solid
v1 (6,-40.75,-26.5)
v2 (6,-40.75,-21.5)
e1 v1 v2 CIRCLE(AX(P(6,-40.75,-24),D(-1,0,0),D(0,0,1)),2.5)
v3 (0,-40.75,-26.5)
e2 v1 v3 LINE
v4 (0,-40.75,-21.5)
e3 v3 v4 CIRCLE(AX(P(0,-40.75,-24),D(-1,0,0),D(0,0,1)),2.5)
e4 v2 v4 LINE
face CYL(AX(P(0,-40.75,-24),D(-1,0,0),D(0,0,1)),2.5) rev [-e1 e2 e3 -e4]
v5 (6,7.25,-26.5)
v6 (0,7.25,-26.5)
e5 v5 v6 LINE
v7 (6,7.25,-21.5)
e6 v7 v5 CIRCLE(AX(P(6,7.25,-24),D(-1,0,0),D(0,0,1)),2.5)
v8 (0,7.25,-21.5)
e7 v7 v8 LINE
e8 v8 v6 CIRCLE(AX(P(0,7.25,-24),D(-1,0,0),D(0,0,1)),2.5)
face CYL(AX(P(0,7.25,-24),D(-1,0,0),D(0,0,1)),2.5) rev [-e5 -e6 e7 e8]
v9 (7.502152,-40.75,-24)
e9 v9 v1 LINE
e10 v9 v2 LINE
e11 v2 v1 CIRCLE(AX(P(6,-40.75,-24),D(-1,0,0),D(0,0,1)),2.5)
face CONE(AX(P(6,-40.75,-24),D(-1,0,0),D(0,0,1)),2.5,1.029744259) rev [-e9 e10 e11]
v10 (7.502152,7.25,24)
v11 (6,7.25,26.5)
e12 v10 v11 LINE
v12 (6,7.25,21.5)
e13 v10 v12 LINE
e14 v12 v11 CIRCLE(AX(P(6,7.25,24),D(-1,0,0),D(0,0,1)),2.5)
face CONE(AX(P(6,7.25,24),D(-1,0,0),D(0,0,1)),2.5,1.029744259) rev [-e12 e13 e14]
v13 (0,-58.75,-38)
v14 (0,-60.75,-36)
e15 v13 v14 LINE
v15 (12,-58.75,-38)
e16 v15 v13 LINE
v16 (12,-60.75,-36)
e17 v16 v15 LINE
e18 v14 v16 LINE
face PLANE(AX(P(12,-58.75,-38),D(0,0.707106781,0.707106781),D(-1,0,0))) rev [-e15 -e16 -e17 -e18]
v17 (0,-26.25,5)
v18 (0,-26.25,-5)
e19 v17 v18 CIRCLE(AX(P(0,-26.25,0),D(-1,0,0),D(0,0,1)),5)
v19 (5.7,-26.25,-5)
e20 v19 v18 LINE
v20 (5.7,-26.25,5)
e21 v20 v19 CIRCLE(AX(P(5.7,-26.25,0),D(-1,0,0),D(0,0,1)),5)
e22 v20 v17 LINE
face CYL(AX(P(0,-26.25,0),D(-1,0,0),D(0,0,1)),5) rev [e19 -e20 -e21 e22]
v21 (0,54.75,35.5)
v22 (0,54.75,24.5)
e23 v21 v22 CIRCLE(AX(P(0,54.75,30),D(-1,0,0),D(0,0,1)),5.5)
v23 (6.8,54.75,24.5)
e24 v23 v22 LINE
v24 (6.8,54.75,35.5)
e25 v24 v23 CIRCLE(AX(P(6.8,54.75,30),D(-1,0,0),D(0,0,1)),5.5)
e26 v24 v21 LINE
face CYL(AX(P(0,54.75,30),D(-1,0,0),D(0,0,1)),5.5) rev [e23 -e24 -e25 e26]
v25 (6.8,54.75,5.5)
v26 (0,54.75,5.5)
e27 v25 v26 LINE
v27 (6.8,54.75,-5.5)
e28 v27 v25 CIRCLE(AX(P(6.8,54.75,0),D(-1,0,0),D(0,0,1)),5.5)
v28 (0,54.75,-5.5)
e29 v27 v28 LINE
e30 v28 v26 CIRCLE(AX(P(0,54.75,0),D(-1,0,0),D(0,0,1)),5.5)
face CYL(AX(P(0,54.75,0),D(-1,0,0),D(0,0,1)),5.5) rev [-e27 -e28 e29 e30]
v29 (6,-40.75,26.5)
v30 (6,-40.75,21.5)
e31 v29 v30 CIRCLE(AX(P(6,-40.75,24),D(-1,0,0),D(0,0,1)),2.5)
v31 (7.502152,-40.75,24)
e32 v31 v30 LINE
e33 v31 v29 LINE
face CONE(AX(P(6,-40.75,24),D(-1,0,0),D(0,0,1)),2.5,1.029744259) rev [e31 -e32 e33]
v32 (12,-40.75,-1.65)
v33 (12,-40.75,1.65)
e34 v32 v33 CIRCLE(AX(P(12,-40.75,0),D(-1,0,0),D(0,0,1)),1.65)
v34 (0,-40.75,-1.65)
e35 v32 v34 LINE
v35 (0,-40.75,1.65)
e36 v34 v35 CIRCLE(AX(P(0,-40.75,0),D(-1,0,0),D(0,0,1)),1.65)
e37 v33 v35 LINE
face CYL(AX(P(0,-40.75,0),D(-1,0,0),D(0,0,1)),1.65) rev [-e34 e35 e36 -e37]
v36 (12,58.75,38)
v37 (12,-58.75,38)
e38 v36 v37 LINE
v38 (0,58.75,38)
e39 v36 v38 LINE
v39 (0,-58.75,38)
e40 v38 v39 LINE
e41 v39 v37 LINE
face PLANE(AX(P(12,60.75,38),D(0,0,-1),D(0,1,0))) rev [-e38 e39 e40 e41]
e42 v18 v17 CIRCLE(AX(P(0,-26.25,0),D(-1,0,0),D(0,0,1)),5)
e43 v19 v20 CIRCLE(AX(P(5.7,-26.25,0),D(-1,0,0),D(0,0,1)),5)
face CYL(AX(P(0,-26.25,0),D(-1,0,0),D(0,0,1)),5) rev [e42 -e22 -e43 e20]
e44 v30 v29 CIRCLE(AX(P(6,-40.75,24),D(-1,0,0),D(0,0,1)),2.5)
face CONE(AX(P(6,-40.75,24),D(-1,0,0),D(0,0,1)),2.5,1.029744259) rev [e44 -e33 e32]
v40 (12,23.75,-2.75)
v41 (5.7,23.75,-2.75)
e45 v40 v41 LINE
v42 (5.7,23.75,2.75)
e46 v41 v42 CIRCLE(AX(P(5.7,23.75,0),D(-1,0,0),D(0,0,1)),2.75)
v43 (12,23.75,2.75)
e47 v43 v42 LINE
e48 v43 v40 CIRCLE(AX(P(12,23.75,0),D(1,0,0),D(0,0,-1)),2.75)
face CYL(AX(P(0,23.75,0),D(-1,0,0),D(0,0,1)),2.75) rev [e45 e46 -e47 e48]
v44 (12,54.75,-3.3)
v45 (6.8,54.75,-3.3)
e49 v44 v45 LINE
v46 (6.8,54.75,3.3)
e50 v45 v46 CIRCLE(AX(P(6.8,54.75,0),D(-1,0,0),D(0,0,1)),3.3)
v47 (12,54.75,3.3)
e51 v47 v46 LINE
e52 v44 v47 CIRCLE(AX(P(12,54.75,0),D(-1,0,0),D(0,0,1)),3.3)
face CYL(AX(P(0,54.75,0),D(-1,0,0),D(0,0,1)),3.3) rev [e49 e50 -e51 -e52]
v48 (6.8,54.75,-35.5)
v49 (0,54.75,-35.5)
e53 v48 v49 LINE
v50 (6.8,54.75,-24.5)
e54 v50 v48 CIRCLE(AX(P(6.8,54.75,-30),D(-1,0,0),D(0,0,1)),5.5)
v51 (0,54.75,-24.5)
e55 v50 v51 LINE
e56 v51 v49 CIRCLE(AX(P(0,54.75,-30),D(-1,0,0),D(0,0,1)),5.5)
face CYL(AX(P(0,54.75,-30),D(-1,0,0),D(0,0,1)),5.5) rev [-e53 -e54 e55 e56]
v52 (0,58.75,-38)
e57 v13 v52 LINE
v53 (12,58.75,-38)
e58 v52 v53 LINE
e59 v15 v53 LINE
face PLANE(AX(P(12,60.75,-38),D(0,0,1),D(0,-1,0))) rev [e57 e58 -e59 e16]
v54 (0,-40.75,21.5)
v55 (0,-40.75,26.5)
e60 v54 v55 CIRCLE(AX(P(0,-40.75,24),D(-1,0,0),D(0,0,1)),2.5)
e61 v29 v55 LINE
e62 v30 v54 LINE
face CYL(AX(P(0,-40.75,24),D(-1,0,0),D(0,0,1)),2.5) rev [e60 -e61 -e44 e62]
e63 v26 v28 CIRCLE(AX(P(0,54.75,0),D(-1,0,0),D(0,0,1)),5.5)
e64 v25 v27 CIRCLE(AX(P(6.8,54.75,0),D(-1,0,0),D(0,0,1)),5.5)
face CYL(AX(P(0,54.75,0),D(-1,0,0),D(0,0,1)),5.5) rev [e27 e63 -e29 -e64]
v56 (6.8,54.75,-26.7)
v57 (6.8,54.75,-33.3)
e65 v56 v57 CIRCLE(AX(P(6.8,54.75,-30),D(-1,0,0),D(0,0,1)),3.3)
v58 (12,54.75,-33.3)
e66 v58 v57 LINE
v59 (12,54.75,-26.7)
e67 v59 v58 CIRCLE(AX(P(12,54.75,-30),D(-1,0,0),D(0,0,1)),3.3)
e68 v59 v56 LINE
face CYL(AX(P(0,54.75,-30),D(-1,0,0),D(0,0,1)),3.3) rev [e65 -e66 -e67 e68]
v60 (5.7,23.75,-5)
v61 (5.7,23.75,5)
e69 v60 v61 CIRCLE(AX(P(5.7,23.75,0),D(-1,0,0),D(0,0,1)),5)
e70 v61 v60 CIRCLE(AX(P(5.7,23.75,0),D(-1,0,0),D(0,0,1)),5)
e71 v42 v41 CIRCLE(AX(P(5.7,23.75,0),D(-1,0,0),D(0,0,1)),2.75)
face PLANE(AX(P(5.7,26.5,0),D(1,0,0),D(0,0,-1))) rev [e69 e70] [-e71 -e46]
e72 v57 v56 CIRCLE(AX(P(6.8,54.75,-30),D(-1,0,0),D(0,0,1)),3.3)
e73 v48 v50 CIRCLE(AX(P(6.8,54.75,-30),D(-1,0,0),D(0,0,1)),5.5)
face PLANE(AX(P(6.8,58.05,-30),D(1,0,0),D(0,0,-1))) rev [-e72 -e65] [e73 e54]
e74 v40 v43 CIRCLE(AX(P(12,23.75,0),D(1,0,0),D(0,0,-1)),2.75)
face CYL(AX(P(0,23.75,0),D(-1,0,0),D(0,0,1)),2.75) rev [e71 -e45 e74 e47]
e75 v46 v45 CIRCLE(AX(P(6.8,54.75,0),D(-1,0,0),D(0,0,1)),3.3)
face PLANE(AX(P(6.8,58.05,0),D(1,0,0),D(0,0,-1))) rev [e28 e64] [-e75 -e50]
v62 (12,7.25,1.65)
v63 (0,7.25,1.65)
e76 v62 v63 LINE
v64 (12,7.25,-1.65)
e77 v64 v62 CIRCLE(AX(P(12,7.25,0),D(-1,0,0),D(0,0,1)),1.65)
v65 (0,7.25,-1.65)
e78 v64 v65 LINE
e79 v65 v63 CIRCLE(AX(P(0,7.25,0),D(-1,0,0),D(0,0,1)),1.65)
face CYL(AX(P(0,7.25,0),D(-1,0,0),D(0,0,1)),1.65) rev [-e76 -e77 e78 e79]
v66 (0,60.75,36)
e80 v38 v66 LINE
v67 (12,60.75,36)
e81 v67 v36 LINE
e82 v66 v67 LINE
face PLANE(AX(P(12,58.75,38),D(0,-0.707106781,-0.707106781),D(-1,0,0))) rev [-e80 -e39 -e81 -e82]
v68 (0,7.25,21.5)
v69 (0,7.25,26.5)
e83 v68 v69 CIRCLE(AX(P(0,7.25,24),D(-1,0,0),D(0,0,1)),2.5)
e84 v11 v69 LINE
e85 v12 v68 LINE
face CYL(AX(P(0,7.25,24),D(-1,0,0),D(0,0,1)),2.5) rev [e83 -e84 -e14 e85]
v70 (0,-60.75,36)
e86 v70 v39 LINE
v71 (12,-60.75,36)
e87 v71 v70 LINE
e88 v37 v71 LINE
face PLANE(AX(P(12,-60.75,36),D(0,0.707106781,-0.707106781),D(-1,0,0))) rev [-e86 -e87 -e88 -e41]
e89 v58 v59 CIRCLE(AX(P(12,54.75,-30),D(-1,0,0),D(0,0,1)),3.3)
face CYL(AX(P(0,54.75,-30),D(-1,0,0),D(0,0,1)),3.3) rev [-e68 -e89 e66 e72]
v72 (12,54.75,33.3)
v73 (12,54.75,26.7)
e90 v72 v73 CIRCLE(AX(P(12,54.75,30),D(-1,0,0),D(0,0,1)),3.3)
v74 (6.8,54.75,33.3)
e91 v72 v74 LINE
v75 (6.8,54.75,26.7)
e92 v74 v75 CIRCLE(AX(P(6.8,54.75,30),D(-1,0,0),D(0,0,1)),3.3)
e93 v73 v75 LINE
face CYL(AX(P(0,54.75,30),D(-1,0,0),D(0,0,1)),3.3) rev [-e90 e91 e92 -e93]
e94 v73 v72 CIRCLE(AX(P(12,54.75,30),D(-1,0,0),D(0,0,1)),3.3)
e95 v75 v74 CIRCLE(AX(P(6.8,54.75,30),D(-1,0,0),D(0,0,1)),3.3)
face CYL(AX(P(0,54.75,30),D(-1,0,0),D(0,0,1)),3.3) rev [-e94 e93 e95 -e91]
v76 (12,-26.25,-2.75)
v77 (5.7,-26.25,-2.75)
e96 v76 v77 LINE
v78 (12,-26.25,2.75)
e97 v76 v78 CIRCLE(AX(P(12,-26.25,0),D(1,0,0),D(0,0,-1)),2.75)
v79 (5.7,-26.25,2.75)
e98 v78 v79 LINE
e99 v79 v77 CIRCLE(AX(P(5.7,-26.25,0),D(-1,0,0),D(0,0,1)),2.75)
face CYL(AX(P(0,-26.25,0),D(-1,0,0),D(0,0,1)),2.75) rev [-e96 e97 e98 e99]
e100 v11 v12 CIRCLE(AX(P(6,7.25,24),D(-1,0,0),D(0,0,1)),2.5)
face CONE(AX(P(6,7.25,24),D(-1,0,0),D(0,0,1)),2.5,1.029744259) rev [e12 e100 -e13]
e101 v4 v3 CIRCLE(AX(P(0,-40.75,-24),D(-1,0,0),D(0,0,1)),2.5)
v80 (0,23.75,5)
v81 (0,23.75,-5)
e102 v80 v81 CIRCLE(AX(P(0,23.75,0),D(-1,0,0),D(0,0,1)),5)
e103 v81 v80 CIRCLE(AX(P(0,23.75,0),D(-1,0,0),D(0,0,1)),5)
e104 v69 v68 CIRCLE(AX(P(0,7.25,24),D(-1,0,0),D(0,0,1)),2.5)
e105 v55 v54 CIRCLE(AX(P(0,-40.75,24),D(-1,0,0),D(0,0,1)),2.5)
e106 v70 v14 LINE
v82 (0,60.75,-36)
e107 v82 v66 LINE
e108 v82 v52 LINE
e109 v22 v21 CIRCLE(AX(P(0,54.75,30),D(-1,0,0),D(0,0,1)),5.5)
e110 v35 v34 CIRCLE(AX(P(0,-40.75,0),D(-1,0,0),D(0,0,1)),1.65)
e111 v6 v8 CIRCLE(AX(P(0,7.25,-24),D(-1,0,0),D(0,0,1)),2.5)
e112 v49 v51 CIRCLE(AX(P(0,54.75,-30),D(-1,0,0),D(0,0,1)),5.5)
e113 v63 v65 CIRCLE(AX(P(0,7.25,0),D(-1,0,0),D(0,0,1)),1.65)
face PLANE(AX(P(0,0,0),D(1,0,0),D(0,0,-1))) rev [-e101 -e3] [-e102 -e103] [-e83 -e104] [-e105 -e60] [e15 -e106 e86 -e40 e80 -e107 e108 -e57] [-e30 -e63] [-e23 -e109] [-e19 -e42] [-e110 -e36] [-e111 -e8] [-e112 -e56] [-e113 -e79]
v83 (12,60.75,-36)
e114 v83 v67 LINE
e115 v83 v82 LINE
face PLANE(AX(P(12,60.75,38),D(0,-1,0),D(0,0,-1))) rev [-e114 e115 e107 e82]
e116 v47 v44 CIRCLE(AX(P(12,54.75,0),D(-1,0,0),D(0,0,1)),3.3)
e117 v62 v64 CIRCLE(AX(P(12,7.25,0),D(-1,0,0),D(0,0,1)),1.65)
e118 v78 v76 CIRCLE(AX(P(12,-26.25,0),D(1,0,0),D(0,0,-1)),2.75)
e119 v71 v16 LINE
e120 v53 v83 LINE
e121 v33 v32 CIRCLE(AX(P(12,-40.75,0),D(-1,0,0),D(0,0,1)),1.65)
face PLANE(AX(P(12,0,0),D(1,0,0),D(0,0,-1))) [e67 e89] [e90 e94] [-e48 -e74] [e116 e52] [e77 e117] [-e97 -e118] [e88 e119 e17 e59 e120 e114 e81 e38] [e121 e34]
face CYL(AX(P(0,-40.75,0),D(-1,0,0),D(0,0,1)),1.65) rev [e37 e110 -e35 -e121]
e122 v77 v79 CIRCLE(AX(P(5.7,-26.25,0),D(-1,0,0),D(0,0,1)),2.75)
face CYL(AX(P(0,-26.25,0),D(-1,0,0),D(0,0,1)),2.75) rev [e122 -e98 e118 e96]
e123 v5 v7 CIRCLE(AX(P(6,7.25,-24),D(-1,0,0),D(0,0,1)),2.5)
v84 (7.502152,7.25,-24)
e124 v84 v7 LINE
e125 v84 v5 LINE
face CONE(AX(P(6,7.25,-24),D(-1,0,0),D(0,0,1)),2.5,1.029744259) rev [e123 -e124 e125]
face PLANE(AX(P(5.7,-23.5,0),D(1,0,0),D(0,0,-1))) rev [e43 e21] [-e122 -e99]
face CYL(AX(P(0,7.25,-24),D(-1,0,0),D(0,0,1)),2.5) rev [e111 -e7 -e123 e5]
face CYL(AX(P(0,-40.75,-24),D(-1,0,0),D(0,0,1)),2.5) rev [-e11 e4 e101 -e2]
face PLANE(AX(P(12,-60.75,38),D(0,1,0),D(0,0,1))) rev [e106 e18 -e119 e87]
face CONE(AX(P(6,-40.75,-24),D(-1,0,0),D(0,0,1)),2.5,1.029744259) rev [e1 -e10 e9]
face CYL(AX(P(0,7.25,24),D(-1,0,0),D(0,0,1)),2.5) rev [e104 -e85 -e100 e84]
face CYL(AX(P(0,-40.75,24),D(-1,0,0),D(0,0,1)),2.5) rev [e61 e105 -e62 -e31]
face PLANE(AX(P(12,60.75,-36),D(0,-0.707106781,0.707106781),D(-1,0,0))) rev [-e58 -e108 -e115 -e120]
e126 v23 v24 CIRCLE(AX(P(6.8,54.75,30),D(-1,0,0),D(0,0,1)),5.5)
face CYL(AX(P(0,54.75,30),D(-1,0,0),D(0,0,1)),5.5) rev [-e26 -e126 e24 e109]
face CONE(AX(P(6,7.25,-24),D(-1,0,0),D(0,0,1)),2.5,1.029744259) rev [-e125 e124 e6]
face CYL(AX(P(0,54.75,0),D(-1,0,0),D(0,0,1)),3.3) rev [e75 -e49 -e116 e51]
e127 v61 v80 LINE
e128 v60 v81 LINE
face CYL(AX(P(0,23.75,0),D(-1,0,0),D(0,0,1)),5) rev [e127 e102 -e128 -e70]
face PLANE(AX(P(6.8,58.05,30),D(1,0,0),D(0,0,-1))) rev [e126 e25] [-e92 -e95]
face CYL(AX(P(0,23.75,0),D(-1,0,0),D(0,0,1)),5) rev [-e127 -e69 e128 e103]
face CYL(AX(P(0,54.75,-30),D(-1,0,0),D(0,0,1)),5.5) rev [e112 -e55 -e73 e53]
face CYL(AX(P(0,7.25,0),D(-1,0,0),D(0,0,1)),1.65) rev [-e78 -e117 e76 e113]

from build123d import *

# Parameters (mm, degrees)
SKETCH_1_W                   = 76
SKETCH_1_H                   = 121.5
EXTRUDE_1_DEPTH              = 12
HOLE_WIZARD_M6_1_D           = 6.6
HOLE_WIZARD_M6_1_CBORE_D     = 11
HOLE_WIZARD_M6_1_CBORE_DEPTH = 6.8
HOLE_WIZARD_M4_1_D           = 3.3
F_5_0MM_1_D                  = 5
F_5_0MM_1_DEPTH              = 6
F_5_0MM_1_TIP                = 1.502151548
HOLE_WIZARD_M5_1_D           = 5.5
HOLE_WIZARD_M5_1_DEPTH       = 12.4
HOLE_WIZARD_M5_1_CBORE_D     = 10
HOLE_WIZARD_M5_1_CBORE_DEPTH = 5.7
HOLE_WIZARD_M5_1_TIP         = 1.652366702
CHAMFER_1_SIZE               = 2


with BuildPart() as part:
    # 草图1 → 凸台-拉伸1 (new body)
    with BuildSketch(Plane(origin=(0, 0, 0), x_dir=(0, 0, -1), z_dir=(1, 0, 0))):
        Rectangle(SKETCH_1_W, SKETCH_1_H)
    extrude(amount=EXTRUDE_1_DEPTH)

    # M6 六角圆柱头螺钉的柱形沉头孔1 (through all)
    with Locations(Plane.ZY):
        with Locations((30, 54.75), (-30, 54.75), (0, 54.75)):
            CounterBoreHole(HOLE_WIZARD_M6_1_D / 2, HOLE_WIZARD_M6_1_CBORE_D / 2, HOLE_WIZARD_M6_1_CBORE_DEPTH)

    # M4 螺纹孔1 (through all)
    with Locations(Plane.ZY):
        with Locations((0, 7.25), (0, -40.75)):
            Hole(HOLE_WIZARD_M4_1_D / 2)

    # Ø5.0mm 暗销孔1
    with Locations(Plane.ZY):
        with Locations((24, 7.25), (24, -40.75), (-24, -40.75), (-24, 7.25)):
            Hole(F_5_0MM_1_D / 2, depth=F_5_0MM_1_DEPTH)
            with Locations((0, 0, -(F_5_0MM_1_DEPTH + F_5_0MM_1_TIP / 2))):  # 118° drill point
                Cone(0, F_5_0MM_1_D / 2, F_5_0MM_1_TIP, mode=Mode.SUBTRACT)

    # M5 六角圆柱头螺钉的柱形沉头孔1
    with Locations(Plane.ZY):
        with Locations((0, 23.75), (0, -26.25)):
            CounterBoreHole(HOLE_WIZARD_M5_1_D / 2, HOLE_WIZARD_M5_1_CBORE_D / 2, HOLE_WIZARD_M5_1_CBORE_DEPTH, depth=HOLE_WIZARD_M5_1_DEPTH)
            with Locations((0, 0, -(HOLE_WIZARD_M5_1_DEPTH + HOLE_WIZARD_M5_1_TIP / 2))):  # 118° drill point
                Cone(0, HOLE_WIZARD_M5_1_D / 2, HOLE_WIZARD_M5_1_TIP, mode=Mode.SUBTRACT)

    # 倒角1
    chamfer_1_edges = [part.edges().sort_by_distance(p)[0] for p in [
        (6, -60.75, -38),
        (6, -60.75, 38),
        (6, 60.75, 38),
        (6, 60.75, -38),
    ]]
    chamfer(chamfer_1_edges, length=CHAMFER_1_SIZE)


solid = part.part
